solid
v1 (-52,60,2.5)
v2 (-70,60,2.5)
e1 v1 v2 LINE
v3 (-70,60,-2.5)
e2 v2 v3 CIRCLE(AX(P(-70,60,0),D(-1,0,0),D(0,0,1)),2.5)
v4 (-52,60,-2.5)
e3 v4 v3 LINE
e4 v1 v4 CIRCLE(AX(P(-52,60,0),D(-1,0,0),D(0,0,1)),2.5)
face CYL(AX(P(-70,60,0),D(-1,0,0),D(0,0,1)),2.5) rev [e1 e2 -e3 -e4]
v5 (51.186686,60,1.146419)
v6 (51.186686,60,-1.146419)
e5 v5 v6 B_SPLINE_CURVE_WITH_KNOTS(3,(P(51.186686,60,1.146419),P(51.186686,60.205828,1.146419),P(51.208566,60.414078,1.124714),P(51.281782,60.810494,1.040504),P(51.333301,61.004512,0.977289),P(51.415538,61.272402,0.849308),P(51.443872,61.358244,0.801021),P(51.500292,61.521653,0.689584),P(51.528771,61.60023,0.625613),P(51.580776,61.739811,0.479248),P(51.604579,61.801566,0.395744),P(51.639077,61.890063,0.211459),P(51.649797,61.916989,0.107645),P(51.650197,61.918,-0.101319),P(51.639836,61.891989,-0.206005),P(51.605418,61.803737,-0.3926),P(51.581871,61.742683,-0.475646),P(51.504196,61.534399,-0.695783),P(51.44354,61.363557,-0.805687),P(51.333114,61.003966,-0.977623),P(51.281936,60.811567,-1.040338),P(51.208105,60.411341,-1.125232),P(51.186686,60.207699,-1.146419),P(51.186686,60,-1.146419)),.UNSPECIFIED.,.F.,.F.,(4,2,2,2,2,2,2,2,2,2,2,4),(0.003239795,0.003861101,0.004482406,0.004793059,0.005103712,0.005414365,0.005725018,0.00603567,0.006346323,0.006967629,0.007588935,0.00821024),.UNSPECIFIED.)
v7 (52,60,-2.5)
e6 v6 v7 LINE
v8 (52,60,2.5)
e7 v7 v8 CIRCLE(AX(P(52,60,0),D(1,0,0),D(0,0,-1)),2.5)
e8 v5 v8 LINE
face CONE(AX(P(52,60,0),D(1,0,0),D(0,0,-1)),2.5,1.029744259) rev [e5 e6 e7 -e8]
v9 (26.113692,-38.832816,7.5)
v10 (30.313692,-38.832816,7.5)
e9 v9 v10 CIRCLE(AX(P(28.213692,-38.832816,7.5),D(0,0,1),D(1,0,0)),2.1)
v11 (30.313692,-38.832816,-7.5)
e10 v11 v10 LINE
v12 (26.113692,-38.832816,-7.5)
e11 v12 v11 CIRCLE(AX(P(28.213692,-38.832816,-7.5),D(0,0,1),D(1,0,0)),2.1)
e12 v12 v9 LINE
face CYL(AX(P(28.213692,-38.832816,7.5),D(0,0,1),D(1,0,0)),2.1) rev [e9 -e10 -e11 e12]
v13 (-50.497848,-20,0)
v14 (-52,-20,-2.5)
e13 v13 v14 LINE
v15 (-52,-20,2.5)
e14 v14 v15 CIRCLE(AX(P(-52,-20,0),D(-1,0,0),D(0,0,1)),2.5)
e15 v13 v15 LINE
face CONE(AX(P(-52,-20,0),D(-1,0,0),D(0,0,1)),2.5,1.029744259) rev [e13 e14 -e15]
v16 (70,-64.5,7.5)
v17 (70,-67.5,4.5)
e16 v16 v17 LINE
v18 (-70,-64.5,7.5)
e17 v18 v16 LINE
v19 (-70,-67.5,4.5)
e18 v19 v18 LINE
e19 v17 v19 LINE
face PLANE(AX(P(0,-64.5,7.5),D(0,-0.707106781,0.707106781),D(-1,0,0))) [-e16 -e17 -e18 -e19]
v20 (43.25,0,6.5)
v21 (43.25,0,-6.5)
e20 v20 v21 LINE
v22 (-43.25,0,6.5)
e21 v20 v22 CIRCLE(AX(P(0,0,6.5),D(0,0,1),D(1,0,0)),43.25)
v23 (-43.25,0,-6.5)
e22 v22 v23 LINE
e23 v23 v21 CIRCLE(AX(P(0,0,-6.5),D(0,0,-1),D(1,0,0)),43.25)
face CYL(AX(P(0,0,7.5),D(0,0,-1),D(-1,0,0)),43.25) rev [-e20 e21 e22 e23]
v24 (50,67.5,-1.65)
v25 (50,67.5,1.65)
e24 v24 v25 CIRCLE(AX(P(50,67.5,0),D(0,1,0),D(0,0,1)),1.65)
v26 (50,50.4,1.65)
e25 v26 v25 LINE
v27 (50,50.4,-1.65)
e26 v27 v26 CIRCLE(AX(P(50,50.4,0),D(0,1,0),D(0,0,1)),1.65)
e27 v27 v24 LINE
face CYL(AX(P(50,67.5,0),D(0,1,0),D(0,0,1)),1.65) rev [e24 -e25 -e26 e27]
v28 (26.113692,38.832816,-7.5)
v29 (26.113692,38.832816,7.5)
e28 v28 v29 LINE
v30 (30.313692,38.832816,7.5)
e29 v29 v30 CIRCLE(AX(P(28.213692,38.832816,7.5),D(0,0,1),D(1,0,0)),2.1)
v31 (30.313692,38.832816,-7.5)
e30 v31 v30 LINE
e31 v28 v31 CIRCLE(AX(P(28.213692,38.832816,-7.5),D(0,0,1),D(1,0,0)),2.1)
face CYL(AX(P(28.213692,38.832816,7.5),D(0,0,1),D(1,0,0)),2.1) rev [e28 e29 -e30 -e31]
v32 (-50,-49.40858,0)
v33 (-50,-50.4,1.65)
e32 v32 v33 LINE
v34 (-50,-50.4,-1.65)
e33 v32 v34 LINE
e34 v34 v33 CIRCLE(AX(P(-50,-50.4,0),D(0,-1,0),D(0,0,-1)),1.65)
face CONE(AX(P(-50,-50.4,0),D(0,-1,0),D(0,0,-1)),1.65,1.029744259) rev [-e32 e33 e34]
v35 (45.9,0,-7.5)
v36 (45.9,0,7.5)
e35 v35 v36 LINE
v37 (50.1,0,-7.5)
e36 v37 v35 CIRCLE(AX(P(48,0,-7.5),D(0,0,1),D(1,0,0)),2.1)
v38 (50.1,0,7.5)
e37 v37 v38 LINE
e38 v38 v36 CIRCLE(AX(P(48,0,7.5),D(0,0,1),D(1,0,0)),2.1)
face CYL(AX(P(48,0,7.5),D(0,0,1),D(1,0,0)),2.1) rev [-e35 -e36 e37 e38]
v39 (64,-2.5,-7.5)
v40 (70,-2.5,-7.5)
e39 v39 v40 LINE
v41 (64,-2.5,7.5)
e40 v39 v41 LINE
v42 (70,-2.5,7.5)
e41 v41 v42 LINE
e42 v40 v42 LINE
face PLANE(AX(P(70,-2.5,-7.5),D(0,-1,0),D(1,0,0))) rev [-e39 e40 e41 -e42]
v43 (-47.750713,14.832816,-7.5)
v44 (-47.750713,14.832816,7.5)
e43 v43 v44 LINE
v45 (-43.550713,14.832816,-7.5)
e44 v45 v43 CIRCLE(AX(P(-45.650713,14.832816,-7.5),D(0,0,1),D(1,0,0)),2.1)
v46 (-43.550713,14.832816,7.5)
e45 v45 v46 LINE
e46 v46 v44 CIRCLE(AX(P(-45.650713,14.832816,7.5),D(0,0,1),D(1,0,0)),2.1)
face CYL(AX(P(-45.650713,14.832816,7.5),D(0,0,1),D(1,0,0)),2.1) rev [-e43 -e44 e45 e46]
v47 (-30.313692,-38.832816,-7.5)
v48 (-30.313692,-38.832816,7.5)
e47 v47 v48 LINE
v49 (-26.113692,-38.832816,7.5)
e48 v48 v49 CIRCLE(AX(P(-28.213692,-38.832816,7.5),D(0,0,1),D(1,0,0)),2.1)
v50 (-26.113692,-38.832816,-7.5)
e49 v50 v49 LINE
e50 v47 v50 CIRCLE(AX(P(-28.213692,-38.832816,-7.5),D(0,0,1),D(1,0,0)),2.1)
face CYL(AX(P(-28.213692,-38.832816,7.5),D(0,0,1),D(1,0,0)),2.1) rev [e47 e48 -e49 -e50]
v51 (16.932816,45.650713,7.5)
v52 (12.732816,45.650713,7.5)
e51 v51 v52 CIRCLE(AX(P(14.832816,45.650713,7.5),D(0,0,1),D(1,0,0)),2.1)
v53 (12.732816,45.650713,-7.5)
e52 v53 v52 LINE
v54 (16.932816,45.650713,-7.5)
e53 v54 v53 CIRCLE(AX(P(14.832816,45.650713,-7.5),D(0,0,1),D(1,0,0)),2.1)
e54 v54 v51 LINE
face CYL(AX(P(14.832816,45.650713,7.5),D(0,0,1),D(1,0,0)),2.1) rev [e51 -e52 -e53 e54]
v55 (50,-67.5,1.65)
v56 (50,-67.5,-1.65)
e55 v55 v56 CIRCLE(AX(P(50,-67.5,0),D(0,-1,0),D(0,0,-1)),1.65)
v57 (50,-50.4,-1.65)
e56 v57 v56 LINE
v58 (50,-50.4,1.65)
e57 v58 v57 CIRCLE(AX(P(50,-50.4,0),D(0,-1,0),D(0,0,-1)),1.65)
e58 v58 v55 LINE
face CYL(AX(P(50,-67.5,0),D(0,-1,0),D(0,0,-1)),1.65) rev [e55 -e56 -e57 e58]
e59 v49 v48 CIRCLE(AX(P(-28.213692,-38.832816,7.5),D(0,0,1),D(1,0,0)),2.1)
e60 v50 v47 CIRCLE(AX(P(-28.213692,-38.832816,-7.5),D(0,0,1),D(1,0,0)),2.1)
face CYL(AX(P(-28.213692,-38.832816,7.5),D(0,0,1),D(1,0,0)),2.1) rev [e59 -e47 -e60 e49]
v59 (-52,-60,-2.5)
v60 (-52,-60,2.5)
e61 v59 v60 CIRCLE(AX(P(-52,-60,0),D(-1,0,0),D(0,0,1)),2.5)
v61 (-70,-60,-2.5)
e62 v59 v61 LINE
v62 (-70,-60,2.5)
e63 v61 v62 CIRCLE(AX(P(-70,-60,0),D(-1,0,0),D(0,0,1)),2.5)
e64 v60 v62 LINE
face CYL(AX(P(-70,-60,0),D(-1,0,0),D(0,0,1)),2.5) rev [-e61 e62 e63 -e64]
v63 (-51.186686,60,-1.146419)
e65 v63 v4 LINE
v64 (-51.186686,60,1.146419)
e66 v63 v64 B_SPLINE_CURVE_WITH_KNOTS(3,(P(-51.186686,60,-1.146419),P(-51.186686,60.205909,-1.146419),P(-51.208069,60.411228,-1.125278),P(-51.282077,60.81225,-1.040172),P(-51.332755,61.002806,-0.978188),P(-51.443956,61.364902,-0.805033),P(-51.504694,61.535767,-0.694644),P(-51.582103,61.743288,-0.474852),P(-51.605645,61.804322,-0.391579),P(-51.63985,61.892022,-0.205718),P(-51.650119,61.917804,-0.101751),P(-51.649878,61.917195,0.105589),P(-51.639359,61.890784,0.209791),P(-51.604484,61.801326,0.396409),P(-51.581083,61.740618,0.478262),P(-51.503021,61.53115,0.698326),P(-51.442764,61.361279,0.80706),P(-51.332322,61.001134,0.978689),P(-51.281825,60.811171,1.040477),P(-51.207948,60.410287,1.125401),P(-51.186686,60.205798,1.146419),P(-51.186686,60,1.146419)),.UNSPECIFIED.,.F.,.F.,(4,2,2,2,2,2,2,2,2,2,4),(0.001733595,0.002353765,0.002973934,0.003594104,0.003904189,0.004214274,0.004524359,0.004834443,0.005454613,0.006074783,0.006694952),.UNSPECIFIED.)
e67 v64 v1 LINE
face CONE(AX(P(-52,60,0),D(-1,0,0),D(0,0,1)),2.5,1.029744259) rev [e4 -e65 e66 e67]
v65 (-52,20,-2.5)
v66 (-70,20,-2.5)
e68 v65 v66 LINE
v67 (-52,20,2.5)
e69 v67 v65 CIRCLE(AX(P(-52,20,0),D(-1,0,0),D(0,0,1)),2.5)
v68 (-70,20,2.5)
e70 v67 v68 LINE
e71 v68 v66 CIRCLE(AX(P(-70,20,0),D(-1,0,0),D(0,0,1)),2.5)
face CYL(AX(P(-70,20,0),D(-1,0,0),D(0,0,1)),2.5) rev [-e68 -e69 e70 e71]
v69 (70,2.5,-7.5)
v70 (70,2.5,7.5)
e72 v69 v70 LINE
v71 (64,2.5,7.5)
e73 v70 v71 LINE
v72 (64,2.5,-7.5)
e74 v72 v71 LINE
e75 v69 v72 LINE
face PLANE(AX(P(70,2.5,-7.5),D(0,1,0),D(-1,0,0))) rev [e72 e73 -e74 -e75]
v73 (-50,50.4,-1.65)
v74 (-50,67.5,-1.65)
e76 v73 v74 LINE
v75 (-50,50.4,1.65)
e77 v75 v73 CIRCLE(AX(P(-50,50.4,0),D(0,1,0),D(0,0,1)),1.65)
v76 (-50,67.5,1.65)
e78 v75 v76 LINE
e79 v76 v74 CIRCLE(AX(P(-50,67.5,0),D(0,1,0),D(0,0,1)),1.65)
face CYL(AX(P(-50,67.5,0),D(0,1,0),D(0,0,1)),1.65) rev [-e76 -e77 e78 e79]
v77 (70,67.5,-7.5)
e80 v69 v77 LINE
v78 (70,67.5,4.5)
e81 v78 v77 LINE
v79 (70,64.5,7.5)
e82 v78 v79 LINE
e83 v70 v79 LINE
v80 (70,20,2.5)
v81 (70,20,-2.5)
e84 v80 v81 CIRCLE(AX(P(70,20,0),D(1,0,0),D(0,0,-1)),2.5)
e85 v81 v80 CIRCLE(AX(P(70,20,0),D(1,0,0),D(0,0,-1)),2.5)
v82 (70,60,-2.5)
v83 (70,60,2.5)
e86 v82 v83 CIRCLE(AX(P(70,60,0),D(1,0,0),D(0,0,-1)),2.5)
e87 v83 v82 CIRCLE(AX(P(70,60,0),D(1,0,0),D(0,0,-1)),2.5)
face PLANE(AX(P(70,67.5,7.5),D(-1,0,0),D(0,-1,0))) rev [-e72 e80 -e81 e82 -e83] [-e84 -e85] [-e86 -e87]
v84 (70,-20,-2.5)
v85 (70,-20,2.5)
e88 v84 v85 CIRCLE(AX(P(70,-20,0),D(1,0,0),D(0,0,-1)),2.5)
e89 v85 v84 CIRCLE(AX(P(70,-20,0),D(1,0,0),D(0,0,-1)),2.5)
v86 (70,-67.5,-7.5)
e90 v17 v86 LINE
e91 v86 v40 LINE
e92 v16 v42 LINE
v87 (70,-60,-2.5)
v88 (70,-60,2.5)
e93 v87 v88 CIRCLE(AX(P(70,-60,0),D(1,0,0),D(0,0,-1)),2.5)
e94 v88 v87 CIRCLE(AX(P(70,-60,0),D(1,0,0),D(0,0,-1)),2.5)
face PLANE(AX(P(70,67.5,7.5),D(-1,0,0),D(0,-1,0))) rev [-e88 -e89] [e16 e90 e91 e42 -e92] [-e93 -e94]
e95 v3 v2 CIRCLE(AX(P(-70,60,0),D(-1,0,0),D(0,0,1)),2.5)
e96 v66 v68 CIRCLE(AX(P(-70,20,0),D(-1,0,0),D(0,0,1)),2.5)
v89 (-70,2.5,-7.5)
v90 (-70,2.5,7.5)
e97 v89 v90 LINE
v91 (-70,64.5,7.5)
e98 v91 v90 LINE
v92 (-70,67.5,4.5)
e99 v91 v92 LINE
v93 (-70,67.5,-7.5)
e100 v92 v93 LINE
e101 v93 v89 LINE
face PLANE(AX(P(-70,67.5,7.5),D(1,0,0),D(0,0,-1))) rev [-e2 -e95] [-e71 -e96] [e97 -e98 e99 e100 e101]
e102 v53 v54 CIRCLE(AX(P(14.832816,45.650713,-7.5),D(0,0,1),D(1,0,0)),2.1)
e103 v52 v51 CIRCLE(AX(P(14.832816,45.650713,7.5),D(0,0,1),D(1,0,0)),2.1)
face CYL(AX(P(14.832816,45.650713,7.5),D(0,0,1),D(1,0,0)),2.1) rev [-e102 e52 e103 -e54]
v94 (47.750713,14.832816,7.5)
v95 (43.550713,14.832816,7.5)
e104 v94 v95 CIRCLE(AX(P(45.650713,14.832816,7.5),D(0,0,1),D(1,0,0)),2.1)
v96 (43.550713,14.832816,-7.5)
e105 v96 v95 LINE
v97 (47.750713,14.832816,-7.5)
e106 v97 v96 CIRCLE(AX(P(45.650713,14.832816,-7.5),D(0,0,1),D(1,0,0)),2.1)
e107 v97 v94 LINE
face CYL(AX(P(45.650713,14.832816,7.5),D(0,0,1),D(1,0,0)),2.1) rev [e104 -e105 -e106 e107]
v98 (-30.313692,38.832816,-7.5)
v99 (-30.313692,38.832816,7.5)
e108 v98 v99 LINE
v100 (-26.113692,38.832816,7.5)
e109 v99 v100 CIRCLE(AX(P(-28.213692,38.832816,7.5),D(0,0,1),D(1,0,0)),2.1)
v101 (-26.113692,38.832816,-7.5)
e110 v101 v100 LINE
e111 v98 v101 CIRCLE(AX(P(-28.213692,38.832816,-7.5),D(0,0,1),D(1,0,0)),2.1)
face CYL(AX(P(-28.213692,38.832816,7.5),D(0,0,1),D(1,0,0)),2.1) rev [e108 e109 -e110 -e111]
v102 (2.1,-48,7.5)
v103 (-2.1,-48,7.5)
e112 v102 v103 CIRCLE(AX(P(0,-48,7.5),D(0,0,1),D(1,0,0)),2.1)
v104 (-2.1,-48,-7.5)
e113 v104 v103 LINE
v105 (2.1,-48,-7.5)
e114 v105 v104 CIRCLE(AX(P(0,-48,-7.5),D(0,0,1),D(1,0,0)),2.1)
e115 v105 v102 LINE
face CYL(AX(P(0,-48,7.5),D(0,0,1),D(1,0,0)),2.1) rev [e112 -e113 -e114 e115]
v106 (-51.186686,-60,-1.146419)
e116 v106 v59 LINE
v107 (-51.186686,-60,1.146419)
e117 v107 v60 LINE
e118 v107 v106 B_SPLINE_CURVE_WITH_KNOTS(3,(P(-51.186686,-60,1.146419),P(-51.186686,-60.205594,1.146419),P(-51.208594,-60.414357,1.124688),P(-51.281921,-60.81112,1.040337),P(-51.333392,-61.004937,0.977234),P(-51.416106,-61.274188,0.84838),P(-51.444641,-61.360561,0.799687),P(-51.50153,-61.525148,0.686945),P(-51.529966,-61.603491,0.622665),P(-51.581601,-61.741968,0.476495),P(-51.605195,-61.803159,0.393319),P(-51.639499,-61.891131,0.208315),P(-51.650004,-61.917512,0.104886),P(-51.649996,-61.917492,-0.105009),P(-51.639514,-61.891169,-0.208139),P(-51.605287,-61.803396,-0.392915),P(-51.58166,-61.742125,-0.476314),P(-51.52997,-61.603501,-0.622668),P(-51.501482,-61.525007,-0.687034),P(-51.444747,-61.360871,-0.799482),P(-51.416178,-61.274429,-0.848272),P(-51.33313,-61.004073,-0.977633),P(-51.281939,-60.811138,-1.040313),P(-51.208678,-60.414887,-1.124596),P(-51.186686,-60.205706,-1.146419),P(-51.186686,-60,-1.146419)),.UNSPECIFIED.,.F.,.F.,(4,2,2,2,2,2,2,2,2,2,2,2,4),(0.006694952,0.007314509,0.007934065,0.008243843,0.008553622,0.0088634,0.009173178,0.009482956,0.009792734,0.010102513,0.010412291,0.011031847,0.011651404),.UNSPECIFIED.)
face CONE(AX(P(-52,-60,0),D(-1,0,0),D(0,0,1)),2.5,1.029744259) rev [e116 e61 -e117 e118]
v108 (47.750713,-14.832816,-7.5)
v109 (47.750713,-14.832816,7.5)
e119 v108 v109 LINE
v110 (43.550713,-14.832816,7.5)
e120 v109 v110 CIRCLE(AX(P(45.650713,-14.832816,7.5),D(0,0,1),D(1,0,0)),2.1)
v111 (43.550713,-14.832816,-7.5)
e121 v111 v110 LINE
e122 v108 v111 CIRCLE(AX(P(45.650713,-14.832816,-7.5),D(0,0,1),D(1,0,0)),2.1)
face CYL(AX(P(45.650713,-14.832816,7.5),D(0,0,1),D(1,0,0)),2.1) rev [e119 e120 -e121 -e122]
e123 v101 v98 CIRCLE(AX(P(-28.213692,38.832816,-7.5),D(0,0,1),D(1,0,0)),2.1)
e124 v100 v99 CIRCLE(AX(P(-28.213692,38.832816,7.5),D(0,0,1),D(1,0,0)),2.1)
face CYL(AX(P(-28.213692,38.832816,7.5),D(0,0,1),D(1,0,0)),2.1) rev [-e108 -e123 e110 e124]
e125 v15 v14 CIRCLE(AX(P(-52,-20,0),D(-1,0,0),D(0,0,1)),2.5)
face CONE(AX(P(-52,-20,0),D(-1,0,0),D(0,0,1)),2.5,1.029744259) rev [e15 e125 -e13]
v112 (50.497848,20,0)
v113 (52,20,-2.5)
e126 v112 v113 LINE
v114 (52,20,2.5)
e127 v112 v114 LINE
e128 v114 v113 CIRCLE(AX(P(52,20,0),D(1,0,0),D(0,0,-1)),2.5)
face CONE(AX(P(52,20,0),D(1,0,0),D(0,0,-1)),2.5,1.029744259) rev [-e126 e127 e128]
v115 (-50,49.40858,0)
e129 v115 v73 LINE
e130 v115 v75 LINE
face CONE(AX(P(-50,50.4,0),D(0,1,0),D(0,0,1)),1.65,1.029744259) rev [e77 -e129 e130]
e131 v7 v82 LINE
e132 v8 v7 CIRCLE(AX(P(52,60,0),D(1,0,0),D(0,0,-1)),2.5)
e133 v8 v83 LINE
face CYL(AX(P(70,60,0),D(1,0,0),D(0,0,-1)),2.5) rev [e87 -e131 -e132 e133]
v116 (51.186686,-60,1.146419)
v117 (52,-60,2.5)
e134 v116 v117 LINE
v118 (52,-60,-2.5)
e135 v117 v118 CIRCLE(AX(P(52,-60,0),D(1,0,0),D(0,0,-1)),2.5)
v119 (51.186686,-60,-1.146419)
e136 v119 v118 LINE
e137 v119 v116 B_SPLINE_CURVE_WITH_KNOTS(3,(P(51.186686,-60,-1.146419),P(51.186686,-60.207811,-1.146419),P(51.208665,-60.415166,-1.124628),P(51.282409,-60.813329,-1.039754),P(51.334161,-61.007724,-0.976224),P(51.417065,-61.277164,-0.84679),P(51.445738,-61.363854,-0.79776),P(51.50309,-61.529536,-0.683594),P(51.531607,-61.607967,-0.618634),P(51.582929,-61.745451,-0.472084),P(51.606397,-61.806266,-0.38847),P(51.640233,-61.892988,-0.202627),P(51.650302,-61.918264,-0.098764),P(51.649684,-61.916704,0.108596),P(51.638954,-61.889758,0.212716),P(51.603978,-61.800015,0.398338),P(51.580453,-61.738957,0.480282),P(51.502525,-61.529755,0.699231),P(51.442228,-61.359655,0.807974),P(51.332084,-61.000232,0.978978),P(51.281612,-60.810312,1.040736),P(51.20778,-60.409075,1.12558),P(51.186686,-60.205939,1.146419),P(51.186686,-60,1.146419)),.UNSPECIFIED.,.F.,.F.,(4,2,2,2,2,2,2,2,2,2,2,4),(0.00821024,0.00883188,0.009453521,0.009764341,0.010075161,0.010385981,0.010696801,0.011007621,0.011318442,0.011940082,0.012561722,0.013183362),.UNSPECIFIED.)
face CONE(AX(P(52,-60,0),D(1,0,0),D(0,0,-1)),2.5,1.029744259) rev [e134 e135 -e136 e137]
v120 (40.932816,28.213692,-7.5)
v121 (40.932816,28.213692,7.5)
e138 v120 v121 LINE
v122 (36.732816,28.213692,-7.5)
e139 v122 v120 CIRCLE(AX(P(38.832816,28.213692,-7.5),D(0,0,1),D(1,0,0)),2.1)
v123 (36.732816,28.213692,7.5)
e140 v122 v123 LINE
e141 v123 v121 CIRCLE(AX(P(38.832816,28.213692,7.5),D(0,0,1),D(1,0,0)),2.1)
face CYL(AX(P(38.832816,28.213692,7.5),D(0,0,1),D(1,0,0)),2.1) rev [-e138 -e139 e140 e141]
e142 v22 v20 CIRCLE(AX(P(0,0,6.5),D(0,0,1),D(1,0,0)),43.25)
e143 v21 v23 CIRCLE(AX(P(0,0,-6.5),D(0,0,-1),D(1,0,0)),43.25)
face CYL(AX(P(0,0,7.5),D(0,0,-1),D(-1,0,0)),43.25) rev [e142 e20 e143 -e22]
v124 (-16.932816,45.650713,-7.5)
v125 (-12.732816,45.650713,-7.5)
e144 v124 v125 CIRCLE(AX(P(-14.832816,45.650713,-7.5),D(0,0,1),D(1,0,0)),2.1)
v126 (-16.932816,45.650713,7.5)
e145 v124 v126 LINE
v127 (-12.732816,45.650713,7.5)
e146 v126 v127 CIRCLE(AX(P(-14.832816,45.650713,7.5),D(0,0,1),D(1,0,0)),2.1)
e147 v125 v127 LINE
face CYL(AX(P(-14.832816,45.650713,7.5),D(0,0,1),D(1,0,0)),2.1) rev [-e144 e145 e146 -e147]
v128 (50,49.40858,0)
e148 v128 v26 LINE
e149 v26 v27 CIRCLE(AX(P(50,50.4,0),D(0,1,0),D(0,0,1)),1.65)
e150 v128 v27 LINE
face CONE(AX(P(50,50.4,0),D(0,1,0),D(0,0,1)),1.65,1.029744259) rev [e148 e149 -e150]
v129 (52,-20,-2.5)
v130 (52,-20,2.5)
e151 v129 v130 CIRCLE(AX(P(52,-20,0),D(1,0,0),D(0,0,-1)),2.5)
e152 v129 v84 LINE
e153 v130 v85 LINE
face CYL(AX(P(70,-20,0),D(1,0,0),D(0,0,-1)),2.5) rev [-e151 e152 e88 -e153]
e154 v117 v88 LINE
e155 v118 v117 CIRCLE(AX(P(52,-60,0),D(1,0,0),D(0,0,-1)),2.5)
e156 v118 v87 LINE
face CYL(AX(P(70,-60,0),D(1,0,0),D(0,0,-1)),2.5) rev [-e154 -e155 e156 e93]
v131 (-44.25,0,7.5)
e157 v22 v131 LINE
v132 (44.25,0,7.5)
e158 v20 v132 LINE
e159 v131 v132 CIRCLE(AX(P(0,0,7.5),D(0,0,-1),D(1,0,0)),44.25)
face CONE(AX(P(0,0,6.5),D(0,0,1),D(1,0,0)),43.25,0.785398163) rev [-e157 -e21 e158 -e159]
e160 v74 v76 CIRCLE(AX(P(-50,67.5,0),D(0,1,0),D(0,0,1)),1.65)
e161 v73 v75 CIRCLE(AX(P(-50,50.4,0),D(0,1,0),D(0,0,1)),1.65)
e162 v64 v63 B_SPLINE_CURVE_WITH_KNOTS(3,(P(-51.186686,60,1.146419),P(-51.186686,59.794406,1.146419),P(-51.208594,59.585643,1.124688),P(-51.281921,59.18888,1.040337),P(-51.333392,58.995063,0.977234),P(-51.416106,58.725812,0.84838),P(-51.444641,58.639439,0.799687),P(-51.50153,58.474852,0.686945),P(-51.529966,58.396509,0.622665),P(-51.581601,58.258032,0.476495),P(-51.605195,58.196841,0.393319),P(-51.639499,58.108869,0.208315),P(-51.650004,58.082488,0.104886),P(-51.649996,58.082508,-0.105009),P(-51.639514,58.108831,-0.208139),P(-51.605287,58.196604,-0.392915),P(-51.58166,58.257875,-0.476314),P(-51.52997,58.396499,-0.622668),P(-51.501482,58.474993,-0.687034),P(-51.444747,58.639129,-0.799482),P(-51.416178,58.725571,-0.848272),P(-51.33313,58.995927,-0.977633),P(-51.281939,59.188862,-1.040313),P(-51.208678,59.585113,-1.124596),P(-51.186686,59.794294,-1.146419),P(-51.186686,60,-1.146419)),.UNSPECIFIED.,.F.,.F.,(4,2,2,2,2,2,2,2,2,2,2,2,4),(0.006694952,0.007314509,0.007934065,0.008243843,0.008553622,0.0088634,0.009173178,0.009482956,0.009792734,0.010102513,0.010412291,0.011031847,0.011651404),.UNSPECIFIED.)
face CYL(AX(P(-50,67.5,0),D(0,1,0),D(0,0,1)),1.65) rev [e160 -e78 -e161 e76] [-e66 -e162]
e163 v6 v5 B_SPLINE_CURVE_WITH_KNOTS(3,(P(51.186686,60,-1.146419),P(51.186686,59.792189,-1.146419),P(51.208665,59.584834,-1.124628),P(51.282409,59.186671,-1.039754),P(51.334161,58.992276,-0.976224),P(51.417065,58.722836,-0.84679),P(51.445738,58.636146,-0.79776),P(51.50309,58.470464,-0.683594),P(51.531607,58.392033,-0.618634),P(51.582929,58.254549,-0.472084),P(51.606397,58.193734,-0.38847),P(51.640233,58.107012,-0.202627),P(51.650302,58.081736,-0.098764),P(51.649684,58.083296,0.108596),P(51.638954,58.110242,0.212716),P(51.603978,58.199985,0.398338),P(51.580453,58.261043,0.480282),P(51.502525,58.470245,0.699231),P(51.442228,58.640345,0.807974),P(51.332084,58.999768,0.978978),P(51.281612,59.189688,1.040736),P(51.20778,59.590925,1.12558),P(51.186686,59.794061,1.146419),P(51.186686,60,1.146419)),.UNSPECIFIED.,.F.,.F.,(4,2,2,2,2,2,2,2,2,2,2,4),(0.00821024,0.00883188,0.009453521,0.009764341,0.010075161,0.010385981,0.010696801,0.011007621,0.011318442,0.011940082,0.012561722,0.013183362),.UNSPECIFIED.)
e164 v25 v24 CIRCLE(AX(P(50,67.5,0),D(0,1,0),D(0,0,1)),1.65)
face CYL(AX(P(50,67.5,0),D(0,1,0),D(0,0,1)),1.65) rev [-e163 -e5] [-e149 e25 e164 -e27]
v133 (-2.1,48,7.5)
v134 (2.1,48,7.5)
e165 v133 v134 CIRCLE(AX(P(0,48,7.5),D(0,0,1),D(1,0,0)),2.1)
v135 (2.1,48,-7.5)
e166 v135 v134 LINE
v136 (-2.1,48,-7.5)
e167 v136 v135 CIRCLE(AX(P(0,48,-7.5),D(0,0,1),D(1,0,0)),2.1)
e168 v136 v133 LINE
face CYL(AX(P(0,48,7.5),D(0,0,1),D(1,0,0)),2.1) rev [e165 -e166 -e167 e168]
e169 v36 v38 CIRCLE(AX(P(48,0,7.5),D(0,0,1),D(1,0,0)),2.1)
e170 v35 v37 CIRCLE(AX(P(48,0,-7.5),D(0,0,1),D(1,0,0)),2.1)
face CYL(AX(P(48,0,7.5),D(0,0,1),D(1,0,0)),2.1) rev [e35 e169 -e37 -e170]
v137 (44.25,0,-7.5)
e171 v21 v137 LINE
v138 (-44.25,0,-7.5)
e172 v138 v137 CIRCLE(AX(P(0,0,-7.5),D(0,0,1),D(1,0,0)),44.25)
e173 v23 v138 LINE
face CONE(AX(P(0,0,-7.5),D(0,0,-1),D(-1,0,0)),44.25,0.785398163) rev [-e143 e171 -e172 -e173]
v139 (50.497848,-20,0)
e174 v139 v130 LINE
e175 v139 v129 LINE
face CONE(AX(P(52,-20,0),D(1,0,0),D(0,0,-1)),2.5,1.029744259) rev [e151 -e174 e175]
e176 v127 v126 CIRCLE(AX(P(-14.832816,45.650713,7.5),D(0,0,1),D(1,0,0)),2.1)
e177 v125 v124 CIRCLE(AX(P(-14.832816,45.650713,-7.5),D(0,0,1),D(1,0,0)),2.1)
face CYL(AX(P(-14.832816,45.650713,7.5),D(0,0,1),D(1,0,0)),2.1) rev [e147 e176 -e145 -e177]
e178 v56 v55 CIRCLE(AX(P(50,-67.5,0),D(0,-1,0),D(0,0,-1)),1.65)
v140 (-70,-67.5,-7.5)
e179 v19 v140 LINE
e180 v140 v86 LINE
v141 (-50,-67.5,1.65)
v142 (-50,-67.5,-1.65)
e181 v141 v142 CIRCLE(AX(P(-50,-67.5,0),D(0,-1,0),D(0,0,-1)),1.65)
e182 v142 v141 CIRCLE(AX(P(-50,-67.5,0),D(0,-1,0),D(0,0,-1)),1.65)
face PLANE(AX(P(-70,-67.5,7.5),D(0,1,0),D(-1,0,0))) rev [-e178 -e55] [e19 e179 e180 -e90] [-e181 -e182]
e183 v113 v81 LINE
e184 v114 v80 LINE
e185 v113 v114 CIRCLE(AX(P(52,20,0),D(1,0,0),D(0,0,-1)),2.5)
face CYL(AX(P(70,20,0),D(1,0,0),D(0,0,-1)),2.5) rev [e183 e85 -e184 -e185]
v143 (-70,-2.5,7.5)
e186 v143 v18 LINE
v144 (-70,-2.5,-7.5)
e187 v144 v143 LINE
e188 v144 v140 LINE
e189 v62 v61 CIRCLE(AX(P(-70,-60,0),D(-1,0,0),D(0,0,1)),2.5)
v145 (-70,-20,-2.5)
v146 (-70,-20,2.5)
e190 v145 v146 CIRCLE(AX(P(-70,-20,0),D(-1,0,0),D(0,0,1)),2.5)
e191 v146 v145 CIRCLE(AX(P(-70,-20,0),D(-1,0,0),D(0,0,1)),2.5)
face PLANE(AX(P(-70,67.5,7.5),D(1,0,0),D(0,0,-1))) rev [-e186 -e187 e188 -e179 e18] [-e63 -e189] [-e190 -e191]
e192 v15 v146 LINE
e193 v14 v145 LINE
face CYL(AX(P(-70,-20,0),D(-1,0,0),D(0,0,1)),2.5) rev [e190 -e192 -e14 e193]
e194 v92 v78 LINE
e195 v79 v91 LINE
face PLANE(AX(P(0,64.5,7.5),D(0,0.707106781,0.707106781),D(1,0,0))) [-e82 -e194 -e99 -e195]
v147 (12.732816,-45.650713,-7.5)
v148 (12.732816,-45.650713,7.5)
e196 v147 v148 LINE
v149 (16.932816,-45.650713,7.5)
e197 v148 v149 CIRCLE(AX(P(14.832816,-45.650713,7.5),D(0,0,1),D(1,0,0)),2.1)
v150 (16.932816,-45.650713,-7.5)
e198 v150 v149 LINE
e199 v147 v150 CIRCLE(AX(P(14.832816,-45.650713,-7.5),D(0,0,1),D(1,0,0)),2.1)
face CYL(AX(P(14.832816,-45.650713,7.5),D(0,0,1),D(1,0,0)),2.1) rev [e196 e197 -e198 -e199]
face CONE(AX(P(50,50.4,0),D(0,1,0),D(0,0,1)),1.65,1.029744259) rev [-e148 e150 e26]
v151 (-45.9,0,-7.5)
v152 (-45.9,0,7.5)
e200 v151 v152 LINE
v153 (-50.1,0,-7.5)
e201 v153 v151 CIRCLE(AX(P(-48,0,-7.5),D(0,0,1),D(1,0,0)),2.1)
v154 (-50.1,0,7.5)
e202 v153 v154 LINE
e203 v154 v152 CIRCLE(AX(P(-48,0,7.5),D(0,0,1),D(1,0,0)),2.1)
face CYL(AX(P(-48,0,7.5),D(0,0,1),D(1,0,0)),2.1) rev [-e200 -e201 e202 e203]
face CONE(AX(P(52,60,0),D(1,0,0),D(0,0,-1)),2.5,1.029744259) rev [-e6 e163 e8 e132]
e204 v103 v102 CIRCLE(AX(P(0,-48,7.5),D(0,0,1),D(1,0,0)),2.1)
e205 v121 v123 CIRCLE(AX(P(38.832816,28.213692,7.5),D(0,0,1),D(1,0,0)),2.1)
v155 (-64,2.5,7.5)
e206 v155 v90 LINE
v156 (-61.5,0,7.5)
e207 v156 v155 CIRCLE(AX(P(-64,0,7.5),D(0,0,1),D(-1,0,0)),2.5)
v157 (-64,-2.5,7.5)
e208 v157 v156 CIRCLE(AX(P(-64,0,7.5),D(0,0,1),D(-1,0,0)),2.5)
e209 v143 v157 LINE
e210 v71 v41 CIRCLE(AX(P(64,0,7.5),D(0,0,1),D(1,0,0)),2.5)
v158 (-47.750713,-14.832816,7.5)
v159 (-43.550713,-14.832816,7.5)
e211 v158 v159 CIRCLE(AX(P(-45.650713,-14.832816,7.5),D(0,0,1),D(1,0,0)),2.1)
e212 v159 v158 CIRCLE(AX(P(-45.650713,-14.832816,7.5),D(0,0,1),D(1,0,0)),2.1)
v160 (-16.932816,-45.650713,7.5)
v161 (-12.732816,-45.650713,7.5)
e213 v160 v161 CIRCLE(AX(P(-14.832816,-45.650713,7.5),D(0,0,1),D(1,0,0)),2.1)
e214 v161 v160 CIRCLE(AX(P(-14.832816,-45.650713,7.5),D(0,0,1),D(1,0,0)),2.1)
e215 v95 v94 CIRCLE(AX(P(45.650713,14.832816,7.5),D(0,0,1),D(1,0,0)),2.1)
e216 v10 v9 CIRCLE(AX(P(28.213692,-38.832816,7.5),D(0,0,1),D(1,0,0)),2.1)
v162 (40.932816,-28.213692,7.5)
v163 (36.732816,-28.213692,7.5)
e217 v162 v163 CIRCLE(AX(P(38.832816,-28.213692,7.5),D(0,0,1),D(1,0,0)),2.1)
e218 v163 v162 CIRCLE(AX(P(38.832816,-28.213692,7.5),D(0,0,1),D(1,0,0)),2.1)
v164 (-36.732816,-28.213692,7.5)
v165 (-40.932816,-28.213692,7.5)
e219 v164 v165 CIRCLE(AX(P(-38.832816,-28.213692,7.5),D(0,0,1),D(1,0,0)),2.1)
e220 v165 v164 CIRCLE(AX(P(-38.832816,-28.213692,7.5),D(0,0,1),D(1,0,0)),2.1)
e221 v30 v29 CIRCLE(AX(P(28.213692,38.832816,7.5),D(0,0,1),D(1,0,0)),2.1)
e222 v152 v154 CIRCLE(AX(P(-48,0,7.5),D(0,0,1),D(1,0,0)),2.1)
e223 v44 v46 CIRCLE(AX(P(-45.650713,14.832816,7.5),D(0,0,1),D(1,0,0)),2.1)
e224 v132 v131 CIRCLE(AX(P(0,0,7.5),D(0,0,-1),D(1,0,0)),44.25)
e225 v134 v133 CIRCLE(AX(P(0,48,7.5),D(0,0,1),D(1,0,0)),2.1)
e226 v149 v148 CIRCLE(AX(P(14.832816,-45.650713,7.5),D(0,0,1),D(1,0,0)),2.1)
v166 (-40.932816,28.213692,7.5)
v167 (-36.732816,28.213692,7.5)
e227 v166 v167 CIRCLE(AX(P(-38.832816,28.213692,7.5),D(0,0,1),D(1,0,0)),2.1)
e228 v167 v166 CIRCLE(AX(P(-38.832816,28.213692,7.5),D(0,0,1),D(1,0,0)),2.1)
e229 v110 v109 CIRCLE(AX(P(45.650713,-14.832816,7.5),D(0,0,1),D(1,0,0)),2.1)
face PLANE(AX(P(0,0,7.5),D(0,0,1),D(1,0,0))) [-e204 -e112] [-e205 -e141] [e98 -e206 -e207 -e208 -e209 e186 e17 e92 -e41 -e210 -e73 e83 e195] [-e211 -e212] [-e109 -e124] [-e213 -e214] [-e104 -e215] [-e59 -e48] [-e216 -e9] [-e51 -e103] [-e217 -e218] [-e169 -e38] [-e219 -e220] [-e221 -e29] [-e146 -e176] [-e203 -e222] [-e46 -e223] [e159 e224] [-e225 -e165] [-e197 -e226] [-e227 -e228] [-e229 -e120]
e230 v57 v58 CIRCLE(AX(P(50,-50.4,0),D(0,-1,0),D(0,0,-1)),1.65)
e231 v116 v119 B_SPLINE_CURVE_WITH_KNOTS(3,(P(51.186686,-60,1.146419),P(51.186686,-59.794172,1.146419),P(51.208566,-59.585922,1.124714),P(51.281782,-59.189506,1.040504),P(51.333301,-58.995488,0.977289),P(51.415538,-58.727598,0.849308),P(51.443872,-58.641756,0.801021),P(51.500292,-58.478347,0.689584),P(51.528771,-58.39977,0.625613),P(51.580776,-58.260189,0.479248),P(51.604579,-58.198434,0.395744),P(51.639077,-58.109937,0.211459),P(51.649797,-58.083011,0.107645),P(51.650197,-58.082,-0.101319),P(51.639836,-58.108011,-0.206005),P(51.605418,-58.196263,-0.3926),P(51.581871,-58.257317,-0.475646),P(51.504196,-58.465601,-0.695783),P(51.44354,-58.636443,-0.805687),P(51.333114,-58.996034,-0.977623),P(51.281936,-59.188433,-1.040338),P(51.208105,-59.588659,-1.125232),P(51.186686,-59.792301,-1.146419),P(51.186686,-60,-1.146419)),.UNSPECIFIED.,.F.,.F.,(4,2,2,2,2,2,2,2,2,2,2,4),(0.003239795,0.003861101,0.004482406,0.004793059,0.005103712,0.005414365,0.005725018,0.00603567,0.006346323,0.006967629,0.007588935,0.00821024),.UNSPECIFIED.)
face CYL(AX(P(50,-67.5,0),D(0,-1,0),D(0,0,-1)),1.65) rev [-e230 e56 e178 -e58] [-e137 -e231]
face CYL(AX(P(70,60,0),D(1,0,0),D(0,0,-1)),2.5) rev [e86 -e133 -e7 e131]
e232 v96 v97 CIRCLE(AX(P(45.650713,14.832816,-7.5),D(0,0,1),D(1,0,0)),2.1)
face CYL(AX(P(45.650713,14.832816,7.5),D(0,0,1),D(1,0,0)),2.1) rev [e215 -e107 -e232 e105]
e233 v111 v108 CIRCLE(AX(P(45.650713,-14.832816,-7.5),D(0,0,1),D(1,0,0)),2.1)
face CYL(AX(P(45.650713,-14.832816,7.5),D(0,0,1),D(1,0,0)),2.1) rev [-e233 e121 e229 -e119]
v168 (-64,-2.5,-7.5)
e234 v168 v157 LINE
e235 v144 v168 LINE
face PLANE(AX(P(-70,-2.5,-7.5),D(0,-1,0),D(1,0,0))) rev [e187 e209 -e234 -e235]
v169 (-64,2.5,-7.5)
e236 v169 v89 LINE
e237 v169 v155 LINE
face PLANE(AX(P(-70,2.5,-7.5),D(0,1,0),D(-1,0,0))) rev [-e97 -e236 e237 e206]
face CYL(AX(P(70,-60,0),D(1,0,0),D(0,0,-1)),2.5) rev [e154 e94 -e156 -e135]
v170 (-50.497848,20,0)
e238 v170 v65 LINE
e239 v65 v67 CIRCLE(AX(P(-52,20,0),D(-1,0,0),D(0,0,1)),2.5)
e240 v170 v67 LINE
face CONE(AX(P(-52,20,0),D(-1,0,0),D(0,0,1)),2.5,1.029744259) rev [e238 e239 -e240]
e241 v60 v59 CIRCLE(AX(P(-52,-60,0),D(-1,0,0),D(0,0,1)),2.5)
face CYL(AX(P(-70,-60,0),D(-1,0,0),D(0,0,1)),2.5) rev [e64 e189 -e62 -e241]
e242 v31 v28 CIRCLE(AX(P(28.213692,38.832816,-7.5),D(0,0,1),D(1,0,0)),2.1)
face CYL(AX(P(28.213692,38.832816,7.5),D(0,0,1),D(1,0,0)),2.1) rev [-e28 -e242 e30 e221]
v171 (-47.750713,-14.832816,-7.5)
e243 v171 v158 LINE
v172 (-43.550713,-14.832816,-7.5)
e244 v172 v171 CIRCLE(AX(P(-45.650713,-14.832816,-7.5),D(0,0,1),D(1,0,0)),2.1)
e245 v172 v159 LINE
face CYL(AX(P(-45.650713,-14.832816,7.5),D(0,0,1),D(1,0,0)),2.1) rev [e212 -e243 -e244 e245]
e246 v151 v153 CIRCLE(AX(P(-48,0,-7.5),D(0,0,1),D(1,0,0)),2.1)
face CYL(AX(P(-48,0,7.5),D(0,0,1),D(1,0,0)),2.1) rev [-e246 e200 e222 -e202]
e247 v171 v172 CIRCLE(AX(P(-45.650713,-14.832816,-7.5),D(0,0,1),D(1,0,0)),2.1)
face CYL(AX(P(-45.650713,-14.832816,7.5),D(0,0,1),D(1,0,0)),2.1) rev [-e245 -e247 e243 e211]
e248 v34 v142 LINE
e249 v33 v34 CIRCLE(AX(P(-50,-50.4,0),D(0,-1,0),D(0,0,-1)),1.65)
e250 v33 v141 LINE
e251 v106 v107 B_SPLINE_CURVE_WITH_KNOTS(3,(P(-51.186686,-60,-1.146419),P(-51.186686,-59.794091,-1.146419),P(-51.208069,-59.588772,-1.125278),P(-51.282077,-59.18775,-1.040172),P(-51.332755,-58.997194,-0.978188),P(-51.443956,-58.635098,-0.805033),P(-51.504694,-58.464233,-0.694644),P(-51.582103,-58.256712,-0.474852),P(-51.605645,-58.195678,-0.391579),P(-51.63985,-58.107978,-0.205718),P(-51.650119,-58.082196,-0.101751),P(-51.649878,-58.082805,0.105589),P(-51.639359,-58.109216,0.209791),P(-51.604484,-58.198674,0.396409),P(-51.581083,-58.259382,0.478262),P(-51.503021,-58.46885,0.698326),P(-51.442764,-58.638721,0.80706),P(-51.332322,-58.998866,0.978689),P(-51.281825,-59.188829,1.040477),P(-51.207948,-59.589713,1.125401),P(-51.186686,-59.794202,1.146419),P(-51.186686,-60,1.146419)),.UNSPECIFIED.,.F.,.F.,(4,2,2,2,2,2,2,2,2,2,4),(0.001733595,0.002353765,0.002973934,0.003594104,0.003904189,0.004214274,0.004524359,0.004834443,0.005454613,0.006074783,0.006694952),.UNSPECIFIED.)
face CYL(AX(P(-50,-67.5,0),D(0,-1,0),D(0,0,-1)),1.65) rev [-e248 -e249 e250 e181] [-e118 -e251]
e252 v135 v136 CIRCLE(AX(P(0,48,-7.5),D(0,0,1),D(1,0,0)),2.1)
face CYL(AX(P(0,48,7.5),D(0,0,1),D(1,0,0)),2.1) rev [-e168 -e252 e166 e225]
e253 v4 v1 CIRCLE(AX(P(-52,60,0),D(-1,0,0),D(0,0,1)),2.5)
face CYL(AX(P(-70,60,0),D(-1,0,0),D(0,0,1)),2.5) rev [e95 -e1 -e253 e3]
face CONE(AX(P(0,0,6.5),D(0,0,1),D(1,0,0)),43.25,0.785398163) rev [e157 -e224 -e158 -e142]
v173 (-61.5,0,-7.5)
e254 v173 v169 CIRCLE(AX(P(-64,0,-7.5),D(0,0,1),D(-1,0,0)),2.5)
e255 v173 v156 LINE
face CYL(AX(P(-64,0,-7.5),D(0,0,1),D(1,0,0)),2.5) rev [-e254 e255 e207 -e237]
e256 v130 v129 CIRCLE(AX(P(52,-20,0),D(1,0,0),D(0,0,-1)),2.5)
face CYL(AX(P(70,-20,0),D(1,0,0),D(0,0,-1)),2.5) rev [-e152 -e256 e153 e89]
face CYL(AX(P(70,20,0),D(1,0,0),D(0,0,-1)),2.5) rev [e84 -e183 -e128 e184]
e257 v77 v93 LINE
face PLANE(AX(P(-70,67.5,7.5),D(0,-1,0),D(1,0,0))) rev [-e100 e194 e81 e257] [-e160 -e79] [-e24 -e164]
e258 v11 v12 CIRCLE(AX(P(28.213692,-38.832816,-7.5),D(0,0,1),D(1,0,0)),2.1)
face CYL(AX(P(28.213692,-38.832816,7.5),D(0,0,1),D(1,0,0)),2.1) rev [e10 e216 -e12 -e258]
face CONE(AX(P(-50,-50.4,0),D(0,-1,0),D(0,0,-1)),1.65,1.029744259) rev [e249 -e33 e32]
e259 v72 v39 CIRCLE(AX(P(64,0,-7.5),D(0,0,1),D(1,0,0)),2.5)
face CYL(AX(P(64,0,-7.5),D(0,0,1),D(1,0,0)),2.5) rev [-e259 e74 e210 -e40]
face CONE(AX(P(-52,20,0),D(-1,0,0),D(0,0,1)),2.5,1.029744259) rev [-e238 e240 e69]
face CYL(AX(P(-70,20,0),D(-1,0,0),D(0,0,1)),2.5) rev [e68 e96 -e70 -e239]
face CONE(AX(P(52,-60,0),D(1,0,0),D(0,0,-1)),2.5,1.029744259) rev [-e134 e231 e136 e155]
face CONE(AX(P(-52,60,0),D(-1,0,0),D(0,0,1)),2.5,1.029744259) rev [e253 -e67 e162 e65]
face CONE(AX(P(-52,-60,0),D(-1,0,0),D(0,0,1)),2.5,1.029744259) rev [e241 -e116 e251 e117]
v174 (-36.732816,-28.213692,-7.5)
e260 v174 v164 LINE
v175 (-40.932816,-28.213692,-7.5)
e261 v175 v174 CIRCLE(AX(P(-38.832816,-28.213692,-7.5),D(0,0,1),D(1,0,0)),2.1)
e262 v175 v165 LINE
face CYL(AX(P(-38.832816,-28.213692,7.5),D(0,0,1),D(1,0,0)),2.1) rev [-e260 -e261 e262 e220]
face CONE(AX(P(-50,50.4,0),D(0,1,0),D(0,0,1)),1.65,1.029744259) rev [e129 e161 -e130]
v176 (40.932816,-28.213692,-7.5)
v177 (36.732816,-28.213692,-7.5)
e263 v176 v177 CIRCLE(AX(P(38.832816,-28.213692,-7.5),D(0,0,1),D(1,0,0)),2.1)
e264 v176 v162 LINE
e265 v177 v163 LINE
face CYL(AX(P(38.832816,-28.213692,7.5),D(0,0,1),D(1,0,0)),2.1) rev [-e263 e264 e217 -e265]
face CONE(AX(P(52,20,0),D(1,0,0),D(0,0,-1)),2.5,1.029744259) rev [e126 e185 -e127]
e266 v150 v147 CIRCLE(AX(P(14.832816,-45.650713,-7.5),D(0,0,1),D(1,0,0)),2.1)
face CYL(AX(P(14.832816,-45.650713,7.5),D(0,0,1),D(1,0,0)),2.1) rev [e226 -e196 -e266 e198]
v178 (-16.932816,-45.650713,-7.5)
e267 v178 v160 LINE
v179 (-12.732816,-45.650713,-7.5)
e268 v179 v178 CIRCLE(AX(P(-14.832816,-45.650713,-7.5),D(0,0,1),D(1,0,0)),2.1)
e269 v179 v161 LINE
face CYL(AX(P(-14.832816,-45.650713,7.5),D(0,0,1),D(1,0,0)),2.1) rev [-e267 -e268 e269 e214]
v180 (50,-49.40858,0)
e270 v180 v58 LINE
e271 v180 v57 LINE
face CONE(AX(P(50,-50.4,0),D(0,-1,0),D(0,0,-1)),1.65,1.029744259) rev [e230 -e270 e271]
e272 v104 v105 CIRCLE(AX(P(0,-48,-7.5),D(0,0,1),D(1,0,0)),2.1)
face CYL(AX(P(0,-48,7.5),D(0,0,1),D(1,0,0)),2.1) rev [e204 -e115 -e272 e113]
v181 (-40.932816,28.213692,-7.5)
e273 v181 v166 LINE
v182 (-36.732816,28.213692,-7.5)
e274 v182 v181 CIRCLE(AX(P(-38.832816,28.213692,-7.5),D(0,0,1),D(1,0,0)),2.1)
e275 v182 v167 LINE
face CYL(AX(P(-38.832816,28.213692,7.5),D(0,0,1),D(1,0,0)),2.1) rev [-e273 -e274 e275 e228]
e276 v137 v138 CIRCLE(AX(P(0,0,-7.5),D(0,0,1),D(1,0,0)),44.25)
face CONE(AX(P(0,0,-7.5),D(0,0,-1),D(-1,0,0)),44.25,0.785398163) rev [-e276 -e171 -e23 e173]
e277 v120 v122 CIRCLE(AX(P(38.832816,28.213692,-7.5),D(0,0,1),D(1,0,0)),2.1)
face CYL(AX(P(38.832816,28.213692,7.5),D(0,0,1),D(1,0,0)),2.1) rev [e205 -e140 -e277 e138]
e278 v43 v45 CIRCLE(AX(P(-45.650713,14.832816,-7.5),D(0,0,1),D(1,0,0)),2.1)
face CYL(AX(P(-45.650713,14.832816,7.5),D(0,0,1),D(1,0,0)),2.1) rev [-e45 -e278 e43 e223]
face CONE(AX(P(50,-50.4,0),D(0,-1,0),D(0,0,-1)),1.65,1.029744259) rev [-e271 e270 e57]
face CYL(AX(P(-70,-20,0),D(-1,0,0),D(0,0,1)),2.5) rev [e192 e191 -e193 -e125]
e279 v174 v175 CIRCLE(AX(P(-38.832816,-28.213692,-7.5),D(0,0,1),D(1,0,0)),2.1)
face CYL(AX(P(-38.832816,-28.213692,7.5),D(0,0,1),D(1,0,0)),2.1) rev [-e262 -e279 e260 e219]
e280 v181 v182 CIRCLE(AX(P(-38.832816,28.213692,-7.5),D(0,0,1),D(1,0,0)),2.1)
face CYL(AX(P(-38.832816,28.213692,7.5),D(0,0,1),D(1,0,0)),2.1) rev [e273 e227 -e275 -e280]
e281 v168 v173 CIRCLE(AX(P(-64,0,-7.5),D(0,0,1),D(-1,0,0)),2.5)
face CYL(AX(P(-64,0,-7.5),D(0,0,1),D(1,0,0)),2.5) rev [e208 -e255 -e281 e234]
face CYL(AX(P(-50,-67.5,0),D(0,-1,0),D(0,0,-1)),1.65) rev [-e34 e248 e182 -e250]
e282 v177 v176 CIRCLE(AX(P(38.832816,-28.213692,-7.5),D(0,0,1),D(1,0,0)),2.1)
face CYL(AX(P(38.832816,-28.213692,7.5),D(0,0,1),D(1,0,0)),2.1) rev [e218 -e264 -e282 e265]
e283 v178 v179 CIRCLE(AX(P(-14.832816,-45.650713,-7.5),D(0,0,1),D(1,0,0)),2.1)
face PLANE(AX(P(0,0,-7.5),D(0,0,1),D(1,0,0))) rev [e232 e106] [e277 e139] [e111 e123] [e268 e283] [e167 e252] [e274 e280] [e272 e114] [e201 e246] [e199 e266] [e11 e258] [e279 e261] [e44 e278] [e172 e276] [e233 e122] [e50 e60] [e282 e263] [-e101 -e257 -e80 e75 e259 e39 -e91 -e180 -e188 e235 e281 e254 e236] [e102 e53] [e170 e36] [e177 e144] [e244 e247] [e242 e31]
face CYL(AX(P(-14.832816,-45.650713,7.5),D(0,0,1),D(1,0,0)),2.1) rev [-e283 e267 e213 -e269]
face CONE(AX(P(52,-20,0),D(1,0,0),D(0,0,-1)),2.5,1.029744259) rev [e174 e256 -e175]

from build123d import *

# Parameters (mm, degrees)
SKETCH_1_W                  = 140
SKETCH_1_H                  = 135
SKETCH_1_R                  = 43.25
EXTRUDE_1_DEPTH             = 7.5
HOLE_WIZARD_M6_1_AT_2_COUNT = 2
HOLE_WIZARD_M6_1_AT_2_PITCH = 40
HOLE_WIZARD_M6_1_AT_3_COUNT = 2
HOLE_WIZARD_M6_1_AT_3_PITCH = 80
HOLE_WIZARD_M6_1_AT_4_COUNT = 2
HOLE_WIZARD_M6_1_AT_4_PITCH = 40
HOLE_WIZARD_M5_1_D          = 4.2
CHAMFER_1_SIZE              = 1
PATTERN_CIRCULAR_1_COUNT    = 20
CUT_EXTRUDE_1_DEPTH         = 99.393343271
HOLE_WIZARD_M4_1_AT_2_COUNT = 2
HOLE_WIZARD_M4_1_AT_2_PITCH = 100
CHAMFER_2_SIZE              = 3


with BuildPart() as part:
    # 草图1 → 凸台-拉伸1 (new, symmetric)
    with BuildSketch(Plane.XY):
        Rectangle(SKETCH_1_W, SKETCH_1_H)
        Circle(SKETCH_1_R, mode=Mode.SUBTRACT)
    extrude(amount=EXTRUDE_1_DEPTH, both=True)

    # 草图3 → M6 螺纹孔1 (revolve, cut)
    with BuildSketch(Plane(origin=(70, -20, 0), x_dir=(0, 0, -1), z_dir=(0, 1, 0))):
        Polygon((0, 0), (0, 19.502151548), (2.5, 18), (2.5, 0), align=None)
    hole_wizard_m6_1 = revolve(axis=Axis((76.35, -20, 0), (-1, 0, 0)), mode=Mode.SUBTRACT)

    # M6 螺纹孔1 at 2: M6 螺纹孔1 ×2
    with Locations(*[(0, -i * HOLE_WIZARD_M6_1_AT_2_PITCH, 0) for i in range(1, HOLE_WIZARD_M6_1_AT_2_COUNT)]):
        add(hole_wizard_m6_1, mode=Mode.SUBTRACT)

    # M6 螺纹孔1 at 3: M6 螺纹孔1 ×2
    with Locations(*[(0, i * HOLE_WIZARD_M6_1_AT_3_PITCH, 0) for i in range(1, HOLE_WIZARD_M6_1_AT_3_COUNT)]):
        add(hole_wizard_m6_1, mode=Mode.SUBTRACT)

    # M6 螺纹孔1 at 4: M6 螺纹孔1 ×2
    with Locations(*[(0, i * HOLE_WIZARD_M6_1_AT_4_PITCH, 0) for i in range(1, HOLE_WIZARD_M6_1_AT_4_COUNT)]):
        add(hole_wizard_m6_1, mode=Mode.SUBTRACT)

    # 镜向2: M6 螺纹孔1 across plane
    add(hole_wizard_m6_1.mirror(Plane(origin=(0, 0, 0), x_dir=(0, 0, 1), z_dir=(1, 0, 0))), mode=Mode.SUBTRACT)

    # 镜向2 copy 1 sketch → 镜向2 copy 1 (revolve, cut)
    with BuildSketch(Plane(origin=(-70, -60, 0), x_dir=(0, 0, -1), z_dir=(0, 1, 0))):
        Polygon((0, 0), (0, -19.502151548), (2.5, -18), (2.5, 0), align=None)
    revolve(axis=Axis((-76.35, -60, 0), (-1, 0, 0)), mode=Mode.SUBTRACT)

    # 镜向2 copy 2 sketch → 镜向2 copy 2 (revolve, cut)
    with BuildSketch(Plane(origin=(-70, 60, 0), x_dir=(0, 0, -1), z_dir=(0, 1, 0))):
        Polygon((0, 0), (0, -19.502151548), (2.5, -18), (2.5, 0), align=None)
    revolve(axis=Axis((-76.35, 60, 0), (-1, 0, 0)), mode=Mode.SUBTRACT)

    # 镜向2 copy 3 sketch → 镜向2 copy 3 (revolve, cut)
    with BuildSketch(Plane(origin=(-70, 20, 0), x_dir=(0, 0, -1), z_dir=(0, 1, 0))):
        Polygon((0, 0), (0, -19.502151548), (2.5, -18), (2.5, 0), align=None)
    revolve(axis=Axis((-76.35, 20, 0), (-1, 0, 0)), mode=Mode.SUBTRACT)

    # M5 螺纹孔1 (through all)
    with Locations(Plane.XY.offset(7.5)):
        with Locations((0, 48)):
            hole_wizard_m5_1 = Hole(HOLE_WIZARD_M5_1_D / 2)

    # 倒角1
    chamfer_1_edges = [part.edges().sort_by_distance(p)[0] for p in [
        (-43.25, 0, -7.5),
        (-43.25, 0, 7.5),
    ]]
    chamfer(chamfer_1_edges, length=CHAMFER_1_SIZE)

    # 阵列(圆周)1: M5 螺纹孔1 ×20 about axis
    pattern_circular_1_axis = Axis((0, 0, 0), (0, 0, 1))
    for i in range(1, PATTERN_CIRCULAR_1_COUNT):
        add(hole_wizard_m5_1.rotate(pattern_circular_1_axis, i * 360 / PATTERN_CIRCULAR_1_COUNT), mode=Mode.SUBTRACT)

    # 草图6 → 切除-拉伸1 (cut, through all)
    with BuildSketch(Plane.XY.offset(7.5)):
        with BuildLine():
            Line((70, 2.5), (64, 2.5))
            ThreePointArc((64, 2.5), (61.5, 0), (64, -2.5))
            Line((64, -2.5), (70, -2.5))
            Line((70, -2.5), (70, 2.5))
        make_face()
        with BuildLine():
            Line((-70, -2.5), (-64, -2.5))
            ThreePointArc((-64, -2.5), (-61.5, 0), (-64, 2.5))
            Line((-64, 2.5), (-70, 2.5))
            Line((-70, 2.5), (-70, -2.5))
        make_face()
    extrude(amount=-CUT_EXTRUDE_1_DEPTH, mode=Mode.SUBTRACT)

    # 草图8 → M4 螺纹孔1 (revolve, cut)
    with BuildSketch(Plane(origin=(-50, -67.5, 0), x_dir=(0, 0, -1), z_dir=(1, 0, 0))):
        Polygon((0, 0), (0, 18.091420021), (1.65, 17.1), (1.65, 0), align=None)
    hole_wizard_m4_1 = revolve(axis=Axis((-50, -73.85, 0), (0, 1, 0)), mode=Mode.SUBTRACT)

    # M4 螺纹孔1 at 2: M4 螺纹孔1 ×2
    with Locations(*[(i * HOLE_WIZARD_M4_1_AT_2_PITCH, 0, 0) for i in range(1, HOLE_WIZARD_M4_1_AT_2_COUNT)]):
        add(hole_wizard_m4_1, mode=Mode.SUBTRACT)

    # 镜向3: M4 螺纹孔1 across plane
    add(hole_wizard_m4_1.mirror(Plane.ZX), mode=Mode.SUBTRACT)

    # 镜向3 copy 1 sketch → 镜向3 copy 1 (revolve, cut)
    with BuildSketch(Plane(origin=(50, 67.5, 0), x_dir=(0, 0, -1), z_dir=(1, 0, 0))):
        Polygon((0, 0), (0, -18.091420021), (1.65, -17.1), (1.65, 0), align=None)
    revolve(axis=Axis((50, 73.85, 0), (0, 1, 0)), mode=Mode.SUBTRACT)

    # 倒角2
    chamfer_2_edges = [part.edges().sort_by_distance(p)[0] for p in [
        (0, 67.5, 7.5),
        (0, -67.5, 7.5),
    ]]
    chamfer(chamfer_2_edges, length=CHAMFER_2_SIZE)


solid = part.part
